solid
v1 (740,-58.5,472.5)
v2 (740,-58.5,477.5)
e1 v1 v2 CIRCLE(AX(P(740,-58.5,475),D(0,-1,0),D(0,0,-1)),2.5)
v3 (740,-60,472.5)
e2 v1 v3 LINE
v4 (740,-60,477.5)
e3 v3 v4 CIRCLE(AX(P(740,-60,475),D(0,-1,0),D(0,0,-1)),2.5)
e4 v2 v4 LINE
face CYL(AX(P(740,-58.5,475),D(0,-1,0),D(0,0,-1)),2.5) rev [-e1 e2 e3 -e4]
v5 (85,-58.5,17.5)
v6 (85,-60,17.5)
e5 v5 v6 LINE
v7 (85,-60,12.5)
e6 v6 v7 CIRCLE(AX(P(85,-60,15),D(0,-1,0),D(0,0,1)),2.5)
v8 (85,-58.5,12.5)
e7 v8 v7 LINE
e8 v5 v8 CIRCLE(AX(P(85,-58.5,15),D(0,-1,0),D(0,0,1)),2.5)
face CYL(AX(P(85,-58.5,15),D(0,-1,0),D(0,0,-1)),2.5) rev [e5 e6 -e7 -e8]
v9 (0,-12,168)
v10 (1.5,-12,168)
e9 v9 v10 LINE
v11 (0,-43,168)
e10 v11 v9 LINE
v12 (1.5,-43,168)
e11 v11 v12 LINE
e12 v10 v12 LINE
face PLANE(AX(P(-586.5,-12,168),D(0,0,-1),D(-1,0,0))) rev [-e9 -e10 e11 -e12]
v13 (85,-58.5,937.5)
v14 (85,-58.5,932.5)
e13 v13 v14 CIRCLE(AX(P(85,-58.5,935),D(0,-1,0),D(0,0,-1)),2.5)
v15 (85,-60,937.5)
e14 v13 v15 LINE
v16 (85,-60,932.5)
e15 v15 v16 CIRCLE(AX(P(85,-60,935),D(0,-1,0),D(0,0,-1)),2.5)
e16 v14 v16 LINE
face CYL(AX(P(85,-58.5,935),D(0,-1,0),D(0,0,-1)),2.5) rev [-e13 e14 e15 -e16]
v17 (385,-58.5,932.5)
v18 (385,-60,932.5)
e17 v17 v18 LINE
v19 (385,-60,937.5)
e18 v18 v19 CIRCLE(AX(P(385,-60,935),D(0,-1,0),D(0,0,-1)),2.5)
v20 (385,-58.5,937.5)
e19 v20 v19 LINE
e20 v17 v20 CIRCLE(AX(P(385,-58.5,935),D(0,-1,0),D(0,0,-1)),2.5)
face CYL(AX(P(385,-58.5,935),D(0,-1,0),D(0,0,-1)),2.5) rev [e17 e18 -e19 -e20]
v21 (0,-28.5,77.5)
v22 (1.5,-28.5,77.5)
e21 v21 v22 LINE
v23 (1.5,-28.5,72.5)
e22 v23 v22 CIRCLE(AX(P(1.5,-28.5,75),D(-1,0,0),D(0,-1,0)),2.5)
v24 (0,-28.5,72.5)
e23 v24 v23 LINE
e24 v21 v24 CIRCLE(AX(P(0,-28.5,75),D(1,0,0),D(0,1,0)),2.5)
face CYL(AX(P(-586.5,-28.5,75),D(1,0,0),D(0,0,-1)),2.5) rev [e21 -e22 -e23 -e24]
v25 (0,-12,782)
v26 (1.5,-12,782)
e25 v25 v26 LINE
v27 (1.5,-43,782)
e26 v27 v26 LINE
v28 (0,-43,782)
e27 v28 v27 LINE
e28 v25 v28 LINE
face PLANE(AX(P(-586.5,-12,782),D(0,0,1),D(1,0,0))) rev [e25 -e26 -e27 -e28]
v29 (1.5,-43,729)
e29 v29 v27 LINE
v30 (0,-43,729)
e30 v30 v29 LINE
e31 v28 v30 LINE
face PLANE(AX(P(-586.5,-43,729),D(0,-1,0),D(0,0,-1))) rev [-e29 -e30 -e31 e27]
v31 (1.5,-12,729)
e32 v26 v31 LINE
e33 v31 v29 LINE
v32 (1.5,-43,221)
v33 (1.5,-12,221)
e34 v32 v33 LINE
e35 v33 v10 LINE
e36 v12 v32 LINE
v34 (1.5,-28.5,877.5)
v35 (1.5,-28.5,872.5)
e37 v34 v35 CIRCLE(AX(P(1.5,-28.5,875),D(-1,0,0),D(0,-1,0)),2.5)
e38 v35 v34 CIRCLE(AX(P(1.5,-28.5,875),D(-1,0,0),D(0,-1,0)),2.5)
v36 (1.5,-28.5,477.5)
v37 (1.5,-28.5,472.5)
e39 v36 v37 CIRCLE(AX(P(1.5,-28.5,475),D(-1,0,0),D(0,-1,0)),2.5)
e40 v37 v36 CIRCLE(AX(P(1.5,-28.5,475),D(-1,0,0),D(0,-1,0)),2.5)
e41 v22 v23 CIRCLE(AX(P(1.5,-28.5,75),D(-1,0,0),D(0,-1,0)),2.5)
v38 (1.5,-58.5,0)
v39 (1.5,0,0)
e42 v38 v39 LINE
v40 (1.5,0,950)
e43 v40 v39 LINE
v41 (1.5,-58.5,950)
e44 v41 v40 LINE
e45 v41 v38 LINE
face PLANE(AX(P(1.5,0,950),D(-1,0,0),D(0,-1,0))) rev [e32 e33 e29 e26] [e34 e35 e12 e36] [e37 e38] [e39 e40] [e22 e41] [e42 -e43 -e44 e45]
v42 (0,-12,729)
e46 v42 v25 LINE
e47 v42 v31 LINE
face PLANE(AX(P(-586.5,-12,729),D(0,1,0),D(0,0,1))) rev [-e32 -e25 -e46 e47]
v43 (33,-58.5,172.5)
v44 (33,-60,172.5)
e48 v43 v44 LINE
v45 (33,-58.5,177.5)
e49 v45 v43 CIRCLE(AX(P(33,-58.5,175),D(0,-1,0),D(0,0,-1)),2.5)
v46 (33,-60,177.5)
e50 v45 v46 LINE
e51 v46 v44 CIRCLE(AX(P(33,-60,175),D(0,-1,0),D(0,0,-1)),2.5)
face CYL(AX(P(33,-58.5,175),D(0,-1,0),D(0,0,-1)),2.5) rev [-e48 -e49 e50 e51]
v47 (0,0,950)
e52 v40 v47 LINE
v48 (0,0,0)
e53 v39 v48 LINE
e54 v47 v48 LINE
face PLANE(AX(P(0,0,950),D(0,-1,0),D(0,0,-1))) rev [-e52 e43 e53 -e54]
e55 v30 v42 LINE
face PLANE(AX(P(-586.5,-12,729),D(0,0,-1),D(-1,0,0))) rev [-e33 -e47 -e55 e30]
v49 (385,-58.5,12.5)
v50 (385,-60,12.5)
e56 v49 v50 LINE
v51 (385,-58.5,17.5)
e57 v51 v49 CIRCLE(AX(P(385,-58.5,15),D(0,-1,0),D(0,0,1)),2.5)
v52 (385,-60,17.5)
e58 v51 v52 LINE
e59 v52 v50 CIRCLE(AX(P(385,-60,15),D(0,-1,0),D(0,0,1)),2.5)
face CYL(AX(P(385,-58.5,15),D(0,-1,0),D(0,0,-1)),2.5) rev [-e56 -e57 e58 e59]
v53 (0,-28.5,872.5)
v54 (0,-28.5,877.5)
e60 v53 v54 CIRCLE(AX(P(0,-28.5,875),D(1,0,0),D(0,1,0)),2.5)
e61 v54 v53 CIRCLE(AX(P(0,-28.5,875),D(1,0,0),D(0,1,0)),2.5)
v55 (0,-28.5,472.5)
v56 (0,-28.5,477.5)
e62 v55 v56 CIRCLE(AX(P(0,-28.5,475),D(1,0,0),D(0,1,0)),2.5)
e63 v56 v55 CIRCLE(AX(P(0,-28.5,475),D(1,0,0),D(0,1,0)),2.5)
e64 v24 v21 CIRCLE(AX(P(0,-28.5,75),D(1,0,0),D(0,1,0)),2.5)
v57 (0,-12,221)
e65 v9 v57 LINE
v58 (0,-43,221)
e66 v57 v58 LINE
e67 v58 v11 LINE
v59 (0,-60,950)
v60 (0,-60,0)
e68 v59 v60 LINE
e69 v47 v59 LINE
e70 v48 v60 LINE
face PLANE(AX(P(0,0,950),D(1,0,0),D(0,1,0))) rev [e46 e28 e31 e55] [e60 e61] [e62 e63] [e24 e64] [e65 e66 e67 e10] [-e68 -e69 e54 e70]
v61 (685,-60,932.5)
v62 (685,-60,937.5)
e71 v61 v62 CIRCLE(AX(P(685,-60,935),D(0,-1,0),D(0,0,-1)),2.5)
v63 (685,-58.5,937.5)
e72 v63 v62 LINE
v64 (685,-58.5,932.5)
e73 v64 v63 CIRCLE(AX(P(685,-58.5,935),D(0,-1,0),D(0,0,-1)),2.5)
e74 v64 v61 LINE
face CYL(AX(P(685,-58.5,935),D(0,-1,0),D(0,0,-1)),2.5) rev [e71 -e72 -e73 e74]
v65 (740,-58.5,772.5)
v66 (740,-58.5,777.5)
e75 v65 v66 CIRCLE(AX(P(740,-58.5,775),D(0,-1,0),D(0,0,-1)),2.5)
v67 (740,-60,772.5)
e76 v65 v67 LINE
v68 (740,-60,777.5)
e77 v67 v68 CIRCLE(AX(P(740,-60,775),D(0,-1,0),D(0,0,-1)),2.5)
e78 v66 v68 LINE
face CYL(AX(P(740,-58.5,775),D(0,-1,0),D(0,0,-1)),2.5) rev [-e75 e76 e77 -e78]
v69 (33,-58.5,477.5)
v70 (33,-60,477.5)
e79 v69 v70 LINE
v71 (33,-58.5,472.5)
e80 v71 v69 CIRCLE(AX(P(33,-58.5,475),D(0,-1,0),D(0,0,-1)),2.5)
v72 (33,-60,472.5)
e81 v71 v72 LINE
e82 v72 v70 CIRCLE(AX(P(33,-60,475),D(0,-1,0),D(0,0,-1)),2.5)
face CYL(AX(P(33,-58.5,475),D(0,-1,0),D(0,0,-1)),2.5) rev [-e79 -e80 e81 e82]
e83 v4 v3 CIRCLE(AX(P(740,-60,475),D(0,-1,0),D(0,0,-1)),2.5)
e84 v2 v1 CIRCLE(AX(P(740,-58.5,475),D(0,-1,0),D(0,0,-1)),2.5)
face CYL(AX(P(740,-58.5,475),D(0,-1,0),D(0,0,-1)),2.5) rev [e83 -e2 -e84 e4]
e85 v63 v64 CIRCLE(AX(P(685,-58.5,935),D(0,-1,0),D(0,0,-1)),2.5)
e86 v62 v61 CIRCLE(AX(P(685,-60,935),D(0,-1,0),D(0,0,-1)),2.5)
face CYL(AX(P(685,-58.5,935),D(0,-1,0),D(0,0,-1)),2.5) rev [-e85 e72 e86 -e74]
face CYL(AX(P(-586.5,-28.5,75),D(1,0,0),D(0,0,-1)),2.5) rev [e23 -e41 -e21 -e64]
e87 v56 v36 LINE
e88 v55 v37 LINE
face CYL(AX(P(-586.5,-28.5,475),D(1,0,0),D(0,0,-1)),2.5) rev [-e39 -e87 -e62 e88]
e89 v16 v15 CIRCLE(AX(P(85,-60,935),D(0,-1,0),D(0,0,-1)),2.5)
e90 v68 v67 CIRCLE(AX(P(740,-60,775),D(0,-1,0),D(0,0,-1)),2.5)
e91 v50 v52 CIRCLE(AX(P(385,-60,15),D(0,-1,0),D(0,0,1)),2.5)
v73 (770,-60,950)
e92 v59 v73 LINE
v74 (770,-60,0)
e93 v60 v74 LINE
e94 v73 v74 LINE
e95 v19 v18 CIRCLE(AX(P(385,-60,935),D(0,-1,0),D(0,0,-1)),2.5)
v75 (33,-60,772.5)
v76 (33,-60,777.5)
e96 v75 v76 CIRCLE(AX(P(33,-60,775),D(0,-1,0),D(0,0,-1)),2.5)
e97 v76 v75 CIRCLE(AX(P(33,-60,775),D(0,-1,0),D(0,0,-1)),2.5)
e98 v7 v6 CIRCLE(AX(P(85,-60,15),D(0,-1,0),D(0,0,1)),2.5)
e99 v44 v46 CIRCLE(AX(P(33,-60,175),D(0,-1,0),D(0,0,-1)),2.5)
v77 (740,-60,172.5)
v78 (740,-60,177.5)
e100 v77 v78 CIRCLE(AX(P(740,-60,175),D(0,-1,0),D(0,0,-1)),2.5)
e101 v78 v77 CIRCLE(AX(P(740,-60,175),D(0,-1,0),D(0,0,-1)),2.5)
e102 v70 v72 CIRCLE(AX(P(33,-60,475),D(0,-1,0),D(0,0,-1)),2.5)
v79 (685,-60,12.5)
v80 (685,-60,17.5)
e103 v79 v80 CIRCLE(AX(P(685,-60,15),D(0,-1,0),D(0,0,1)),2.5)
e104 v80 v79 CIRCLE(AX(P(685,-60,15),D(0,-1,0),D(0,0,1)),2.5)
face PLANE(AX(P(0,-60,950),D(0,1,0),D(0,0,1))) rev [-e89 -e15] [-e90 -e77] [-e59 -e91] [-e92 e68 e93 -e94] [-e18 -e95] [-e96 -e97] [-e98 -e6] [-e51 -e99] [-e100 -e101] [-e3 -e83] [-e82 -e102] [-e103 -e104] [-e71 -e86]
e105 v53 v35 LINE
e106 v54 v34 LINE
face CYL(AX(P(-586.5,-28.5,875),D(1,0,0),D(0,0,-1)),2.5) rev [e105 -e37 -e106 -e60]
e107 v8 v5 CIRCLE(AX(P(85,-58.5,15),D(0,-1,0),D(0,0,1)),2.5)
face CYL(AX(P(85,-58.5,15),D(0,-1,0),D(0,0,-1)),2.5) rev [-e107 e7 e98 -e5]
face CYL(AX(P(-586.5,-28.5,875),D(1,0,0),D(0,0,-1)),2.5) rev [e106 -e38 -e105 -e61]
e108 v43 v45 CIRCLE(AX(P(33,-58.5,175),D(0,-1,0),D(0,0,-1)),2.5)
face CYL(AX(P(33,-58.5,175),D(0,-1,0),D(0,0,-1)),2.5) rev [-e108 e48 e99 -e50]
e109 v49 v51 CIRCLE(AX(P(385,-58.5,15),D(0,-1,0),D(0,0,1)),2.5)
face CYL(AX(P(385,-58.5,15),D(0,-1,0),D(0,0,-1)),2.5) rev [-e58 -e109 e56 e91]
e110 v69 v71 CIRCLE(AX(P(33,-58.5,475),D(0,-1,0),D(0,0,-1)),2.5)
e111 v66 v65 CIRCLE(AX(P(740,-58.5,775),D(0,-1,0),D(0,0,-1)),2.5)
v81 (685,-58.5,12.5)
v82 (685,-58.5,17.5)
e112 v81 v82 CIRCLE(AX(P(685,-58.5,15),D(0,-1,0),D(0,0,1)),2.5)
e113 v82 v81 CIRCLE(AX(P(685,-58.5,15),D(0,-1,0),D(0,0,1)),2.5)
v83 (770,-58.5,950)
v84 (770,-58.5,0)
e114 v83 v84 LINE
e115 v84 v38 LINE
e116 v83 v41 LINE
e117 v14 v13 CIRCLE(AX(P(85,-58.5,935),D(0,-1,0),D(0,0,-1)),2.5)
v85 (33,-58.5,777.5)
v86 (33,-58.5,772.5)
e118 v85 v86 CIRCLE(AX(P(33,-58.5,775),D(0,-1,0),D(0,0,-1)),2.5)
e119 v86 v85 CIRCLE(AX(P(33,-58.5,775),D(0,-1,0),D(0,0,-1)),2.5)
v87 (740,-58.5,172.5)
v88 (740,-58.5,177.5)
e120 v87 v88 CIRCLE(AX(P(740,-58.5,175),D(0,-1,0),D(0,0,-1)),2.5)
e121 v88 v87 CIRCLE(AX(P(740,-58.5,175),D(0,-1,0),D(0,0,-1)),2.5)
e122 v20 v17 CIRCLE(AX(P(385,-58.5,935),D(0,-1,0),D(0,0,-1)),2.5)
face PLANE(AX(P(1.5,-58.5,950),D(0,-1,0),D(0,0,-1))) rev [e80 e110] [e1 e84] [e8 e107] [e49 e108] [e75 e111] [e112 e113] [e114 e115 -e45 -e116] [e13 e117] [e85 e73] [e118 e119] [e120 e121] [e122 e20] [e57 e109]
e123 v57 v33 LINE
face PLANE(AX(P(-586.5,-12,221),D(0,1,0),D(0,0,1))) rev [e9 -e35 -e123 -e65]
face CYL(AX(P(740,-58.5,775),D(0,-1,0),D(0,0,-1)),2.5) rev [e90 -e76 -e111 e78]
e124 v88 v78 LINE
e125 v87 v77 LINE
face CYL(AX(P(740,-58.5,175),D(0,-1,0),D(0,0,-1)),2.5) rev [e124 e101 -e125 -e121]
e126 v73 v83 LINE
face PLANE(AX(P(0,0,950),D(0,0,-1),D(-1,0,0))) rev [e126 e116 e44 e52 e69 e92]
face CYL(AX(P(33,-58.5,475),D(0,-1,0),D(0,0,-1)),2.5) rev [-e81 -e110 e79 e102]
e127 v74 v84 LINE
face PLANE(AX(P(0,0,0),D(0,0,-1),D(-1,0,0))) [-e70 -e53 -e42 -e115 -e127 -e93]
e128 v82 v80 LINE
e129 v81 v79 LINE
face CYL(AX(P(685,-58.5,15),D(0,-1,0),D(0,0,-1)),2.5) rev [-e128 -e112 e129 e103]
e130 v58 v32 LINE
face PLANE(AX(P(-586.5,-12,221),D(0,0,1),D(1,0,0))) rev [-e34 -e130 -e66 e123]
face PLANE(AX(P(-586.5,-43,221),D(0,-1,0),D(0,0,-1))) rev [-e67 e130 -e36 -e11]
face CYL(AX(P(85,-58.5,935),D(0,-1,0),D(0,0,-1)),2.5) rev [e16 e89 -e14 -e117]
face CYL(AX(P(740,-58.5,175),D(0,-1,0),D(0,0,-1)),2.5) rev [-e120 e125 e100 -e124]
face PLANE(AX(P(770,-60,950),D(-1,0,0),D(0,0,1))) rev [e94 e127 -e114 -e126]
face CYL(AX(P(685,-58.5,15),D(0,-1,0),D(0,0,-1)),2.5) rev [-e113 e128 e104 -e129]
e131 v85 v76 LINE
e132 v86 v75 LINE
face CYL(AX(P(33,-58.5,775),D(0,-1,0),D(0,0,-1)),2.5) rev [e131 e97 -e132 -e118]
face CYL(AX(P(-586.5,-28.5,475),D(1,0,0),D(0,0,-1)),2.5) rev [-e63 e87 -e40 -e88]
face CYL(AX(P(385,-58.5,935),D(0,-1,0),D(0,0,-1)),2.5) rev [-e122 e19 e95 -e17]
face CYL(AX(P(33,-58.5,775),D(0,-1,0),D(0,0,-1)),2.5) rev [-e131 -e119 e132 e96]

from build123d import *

# Parameters (mm, degrees)
BOSS_EXTRUDE1_DEPTH = 950
SKETCH2_R           = 2.5
SKETCH2_W           = 53
SKETCH2_H           = 31
CUT_EXTRUDE1_DEPTH  = 1356.5
SKETCH3_R           = 2.5
CUT_EXTRUDE2_DEPTH  = 1.5
SKETCH5_W           = 1.5
SKETCH5_H           = 950
CUT_EXTRUDE4_DEPTH  = 58.5


with BuildPart() as part:
    # Sketch1 → Boss-Extrude1 (new body)
    with BuildSketch(Plane.XY):
        Polygon((0, 0), (0, -60), (770, -60), (770, 0), (768.5, 0), (768.5, -58.5), (1.5, -58.5), (1.5, 0), align=None)
    extrude(amount=BOSS_EXTRUDE1_DEPTH)

    # Sketch2 → Cut-Extrude1 (cut)
    with BuildSketch(Plane(origin=(770, 0, 0), x_dir=(0, 0, -1), z_dir=(1, 0, 0))):
        with Locations(Location((-75, -28.5, 0), (0, 0, 270))):
            Circle(SKETCH2_R)
        with Locations(Location((-475, -28.5, 0), (0, 0, 270))):
            Circle(SKETCH2_R)
        with Locations(Location((-875, -28.5, 0), (0, 0, 270))):
            Circle(SKETCH2_R)
        with Locations((-194.5, -27.5)):
            Rectangle(SKETCH2_W, SKETCH2_H)
        with Locations((-755.5, -27.5)):
            Rectangle(SKETCH2_W, SKETCH2_H)
    extrude(amount=-CUT_EXTRUDE1_DEPTH, mode=Mode.SUBTRACT)

    # Sketch3 → Cut-Extrude2 (cut)
    with BuildSketch(Plane.XZ.offset(60)):
        with Locations(Location((740, 475, 0), (0, 0, 270))):
            Circle(SKETCH3_R)
        with Locations(Location((740, 775, 0), (0, 0, 270))):
            Circle(SKETCH3_R)
        with Locations(Location((740, 175, 0), (0, 0, 270))):
            Circle(SKETCH3_R)
        with Locations(Location((33, 775, 0), (0, 0, 270))):
            Circle(SKETCH3_R)
        with Locations(Location((33, 475, 0), (0, 0, 270))):
            Circle(SKETCH3_R)
        with Locations(Location((33, 175, 0), (0, 0, 270))):
            Circle(SKETCH3_R)
        with Locations(Location((385, 935, 0), (0, 0, 270))):
            Circle(SKETCH3_R)
        with Locations(Location((685, 935, 0), (0, 0, 270))):
            Circle(SKETCH3_R)
        with Locations(Location((85, 935, 0), (0, 0, 270))):
            Circle(SKETCH3_R)
        with Locations(Location((85, 15, 0), (0, 0, 90))):
            Circle(SKETCH3_R)
        with Locations(Location((685, 15, 0), (0, 0, 90))):
            Circle(SKETCH3_R)
        with Locations(Location((385, 15, 0), (0, 0, 90))):
            Circle(SKETCH3_R)
    extrude(amount=-CUT_EXTRUDE2_DEPTH, mode=Mode.SUBTRACT)

    # Sketch5 → Cut-Extrude4 (cut)
    with BuildSketch(Plane(origin=(0, 0, 0), x_dir=(1, 0, 0), z_dir=(0, 1, 0))):
        with Locations((769.25, -475)):
            Rectangle(SKETCH5_W, SKETCH5_H)
    extrude(amount=-CUT_EXTRUDE4_DEPTH, mode=Mode.SUBTRACT)


solid = part.part
